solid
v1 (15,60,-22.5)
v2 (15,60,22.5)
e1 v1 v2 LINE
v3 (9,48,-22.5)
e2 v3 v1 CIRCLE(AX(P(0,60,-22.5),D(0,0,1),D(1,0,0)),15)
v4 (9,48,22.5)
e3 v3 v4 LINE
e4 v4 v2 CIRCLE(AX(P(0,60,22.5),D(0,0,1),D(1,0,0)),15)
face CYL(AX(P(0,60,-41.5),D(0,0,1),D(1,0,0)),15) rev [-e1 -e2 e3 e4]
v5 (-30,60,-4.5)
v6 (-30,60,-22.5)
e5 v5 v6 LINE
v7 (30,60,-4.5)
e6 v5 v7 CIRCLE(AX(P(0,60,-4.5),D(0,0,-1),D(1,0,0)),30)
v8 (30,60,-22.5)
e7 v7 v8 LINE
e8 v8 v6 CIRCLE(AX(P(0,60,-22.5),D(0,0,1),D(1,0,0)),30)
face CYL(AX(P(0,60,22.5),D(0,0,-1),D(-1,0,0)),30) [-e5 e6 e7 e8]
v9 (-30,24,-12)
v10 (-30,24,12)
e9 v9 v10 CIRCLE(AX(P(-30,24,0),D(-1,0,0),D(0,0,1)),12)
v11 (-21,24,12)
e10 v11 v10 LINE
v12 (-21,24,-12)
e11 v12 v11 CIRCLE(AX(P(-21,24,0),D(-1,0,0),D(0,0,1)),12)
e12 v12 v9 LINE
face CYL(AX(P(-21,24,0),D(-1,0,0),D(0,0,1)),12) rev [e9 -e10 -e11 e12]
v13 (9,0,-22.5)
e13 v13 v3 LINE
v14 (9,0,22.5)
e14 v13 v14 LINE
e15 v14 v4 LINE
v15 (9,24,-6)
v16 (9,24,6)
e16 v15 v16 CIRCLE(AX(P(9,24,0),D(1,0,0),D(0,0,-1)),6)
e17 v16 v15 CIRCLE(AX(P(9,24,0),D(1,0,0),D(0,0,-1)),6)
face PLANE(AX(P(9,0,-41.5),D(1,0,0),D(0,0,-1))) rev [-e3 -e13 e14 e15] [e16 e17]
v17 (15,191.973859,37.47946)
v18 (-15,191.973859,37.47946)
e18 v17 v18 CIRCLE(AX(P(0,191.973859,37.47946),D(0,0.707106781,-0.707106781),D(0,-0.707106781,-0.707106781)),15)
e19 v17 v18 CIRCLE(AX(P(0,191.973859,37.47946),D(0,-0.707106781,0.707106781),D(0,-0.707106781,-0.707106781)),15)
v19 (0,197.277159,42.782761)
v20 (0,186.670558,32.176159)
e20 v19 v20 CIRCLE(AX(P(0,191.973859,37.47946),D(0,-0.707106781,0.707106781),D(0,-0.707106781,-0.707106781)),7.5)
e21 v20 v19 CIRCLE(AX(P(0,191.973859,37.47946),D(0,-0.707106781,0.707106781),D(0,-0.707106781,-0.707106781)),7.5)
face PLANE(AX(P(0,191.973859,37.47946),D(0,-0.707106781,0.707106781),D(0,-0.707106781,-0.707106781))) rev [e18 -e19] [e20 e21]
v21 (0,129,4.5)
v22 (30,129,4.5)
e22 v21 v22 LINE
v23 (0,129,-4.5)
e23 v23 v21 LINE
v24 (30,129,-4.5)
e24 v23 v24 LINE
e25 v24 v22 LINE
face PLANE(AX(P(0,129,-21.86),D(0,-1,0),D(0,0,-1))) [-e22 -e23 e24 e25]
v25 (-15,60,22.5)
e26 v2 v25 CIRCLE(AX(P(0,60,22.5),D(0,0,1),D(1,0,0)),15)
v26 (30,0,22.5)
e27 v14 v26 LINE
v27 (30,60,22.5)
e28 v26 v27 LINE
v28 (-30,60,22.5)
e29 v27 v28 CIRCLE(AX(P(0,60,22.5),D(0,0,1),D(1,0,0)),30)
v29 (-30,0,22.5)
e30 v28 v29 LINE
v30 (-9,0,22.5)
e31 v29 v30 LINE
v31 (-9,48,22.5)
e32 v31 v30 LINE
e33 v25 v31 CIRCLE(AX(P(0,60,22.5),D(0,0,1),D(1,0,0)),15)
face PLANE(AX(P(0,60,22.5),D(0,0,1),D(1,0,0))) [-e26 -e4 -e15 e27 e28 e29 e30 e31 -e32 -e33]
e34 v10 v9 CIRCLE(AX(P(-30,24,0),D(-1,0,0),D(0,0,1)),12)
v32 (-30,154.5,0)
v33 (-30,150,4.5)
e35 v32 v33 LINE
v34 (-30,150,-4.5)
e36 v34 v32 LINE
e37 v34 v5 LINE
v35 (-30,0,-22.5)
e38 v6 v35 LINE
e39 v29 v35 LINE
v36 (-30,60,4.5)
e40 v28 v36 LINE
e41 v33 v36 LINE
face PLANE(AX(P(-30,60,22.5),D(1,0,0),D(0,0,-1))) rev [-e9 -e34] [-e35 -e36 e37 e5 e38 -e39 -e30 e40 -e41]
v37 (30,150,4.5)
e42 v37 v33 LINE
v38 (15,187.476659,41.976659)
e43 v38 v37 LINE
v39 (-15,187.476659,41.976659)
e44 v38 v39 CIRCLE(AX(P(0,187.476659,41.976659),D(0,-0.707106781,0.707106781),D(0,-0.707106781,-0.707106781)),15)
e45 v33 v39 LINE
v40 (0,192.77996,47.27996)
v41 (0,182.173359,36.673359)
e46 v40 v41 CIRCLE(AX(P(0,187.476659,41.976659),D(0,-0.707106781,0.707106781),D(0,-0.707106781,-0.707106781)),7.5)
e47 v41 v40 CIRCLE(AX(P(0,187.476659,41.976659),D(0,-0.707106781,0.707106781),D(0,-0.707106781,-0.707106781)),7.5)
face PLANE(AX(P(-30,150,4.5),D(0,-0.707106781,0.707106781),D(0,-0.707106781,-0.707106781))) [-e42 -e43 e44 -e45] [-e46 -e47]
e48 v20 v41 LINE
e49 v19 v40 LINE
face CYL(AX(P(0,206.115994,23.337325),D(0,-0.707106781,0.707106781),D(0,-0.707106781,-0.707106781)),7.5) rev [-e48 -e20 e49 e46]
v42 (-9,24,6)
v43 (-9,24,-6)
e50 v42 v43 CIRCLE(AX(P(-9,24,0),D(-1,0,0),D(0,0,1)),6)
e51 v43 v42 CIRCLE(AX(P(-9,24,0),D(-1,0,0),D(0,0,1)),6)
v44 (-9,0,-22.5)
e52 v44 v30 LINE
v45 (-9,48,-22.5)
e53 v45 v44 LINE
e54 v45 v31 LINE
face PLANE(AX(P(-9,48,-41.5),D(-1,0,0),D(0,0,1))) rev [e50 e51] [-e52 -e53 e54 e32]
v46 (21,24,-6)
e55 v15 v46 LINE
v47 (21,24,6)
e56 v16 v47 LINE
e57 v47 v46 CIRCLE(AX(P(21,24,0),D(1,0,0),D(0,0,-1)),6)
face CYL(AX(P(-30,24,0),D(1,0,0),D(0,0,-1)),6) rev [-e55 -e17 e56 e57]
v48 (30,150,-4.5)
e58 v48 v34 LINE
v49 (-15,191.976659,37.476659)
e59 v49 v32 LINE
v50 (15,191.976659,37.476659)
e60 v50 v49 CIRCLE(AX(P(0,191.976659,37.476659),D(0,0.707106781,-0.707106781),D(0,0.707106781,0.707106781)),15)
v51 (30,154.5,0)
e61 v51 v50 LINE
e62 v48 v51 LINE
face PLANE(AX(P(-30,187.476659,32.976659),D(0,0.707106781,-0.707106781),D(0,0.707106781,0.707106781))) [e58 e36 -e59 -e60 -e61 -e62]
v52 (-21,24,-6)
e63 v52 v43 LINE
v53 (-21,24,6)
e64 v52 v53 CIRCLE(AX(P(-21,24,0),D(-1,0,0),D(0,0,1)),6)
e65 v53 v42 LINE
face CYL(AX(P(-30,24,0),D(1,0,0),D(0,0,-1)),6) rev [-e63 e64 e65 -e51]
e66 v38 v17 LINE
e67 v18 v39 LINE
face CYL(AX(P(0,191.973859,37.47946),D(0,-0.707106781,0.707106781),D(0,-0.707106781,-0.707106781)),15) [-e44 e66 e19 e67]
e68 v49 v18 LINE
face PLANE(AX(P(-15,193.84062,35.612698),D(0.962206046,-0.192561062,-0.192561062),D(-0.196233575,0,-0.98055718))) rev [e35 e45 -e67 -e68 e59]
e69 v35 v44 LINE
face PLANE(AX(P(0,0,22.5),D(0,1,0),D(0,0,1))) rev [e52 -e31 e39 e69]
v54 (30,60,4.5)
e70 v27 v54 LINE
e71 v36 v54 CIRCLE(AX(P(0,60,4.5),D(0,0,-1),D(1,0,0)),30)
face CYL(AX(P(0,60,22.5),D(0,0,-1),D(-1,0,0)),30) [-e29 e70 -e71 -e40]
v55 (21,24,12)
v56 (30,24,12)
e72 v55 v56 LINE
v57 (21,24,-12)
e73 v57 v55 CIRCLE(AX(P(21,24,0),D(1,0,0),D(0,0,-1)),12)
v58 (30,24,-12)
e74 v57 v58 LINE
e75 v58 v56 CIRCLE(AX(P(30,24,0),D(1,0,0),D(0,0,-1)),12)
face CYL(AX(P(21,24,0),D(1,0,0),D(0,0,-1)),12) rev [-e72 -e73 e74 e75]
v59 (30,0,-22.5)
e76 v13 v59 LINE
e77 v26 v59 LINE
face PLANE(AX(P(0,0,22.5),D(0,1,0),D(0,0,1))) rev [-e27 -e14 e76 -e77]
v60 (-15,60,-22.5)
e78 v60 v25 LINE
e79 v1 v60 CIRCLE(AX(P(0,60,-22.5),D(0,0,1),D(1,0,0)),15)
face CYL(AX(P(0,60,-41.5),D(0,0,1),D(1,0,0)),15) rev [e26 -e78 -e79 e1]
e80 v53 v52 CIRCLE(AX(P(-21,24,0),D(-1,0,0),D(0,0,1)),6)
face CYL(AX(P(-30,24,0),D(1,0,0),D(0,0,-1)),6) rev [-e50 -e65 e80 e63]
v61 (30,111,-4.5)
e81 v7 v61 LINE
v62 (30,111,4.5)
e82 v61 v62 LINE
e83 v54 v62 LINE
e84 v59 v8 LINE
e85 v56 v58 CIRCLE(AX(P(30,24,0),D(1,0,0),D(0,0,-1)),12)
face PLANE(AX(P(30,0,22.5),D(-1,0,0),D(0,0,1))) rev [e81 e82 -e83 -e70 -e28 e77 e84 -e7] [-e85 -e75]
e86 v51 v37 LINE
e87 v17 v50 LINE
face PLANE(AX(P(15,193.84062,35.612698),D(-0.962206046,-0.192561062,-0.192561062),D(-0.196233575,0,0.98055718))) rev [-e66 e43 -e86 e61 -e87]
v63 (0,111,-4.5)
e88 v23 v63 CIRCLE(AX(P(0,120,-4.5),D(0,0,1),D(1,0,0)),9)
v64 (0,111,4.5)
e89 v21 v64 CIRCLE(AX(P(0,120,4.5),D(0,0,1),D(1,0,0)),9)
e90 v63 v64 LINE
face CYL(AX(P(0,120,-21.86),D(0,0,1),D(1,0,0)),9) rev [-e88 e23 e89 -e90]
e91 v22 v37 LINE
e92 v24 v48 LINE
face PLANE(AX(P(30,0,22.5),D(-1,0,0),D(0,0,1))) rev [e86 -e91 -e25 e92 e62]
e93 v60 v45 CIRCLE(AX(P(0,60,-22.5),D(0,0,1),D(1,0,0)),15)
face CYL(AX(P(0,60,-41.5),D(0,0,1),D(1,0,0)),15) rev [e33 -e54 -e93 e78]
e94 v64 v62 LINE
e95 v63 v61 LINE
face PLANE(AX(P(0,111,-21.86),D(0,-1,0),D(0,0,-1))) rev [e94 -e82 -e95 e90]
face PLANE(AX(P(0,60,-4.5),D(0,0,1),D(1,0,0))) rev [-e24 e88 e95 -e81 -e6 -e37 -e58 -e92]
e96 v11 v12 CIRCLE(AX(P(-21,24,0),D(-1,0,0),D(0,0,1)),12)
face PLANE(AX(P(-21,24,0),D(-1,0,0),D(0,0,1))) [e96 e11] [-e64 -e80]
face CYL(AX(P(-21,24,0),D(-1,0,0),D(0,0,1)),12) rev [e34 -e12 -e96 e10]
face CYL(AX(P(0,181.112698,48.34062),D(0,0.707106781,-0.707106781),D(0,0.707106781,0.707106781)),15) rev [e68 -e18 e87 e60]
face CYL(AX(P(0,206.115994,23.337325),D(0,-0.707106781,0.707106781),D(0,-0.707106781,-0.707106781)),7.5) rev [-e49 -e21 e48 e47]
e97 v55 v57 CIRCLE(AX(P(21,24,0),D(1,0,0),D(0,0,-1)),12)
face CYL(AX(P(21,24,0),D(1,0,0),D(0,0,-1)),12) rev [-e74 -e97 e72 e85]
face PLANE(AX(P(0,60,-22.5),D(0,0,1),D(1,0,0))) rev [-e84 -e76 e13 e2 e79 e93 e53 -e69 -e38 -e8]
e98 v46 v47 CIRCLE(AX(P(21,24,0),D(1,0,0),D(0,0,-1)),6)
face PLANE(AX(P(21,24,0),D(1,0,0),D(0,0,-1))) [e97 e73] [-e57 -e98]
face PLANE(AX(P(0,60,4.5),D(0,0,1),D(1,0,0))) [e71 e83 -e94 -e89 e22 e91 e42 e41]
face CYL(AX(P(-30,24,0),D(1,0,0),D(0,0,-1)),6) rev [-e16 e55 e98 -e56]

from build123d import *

# Parameters (mm, degrees)
CLEVIS_BLOCK_DEPTH         = 22.5
FORK_SLOT_DEPTH            = 64
SIDE_HOLE_A_PROFILE_R      = 12
SIDE_HOLE_A_DEPTH          = 9
SIDE_START                 = -9
SIDE_HOLE_B_PROFILE_R      = 12
SIDE_HOLE_B_DEPTH          = 9
CROSS_HOLE_PROFILE_R       = 6
CROSS_HOLE_DEPTH           = 51
ARM_PLATE_DEPTH            = 4.5
BRACKET_WEB_DEPTH          = 60
PIN_BOSS_PROFILE_R         = 15
PIN_BOSS_DEPTH             = 9
HOOK_SLOT_DEPTH            = 9
BOSS_START                 = -2
BOSS_RECESS_PROFILE_R      = 15
BOSS_RECESS_2MM_DEPTH      = 2
BOSS_START_2               = -16
BOSS_BORE_PROFILE_R        = 15
BOSS_BORE_DEPTH            = 16
BORE_INSERT_BOSS_PROFILE_R = 15
BORE_INSERT_BOSS_DEPTH     = 6.36
INSERT_BORE_PROFILE_R      = 7.5
INSERT_BORE_DEPTH          = 26.36
ARM_TRIM_CUT_DEPTH         = 26.36


with BuildPart() as part:
    # Clevis Block Profile → Clevis Block (new, symmetric)
    with BuildSketch(Plane.XY):
        with BuildLine():
            Line((0, 0), (30, 0))
            Line((30, 0), (30, 60))
            ThreePointArc((30, 60), (0, 90), (-30, 60))
            Line((-30, 60), (-30, 0))
            Line((-30, 0), (0, 0))
        make_face()
    extrude(amount=CLEVIS_BLOCK_DEPTH, both=True)

    # Fork Slot Profile → Fork Slot (cut)
    with BuildSketch(Plane.XY.offset(22.5)):
        with BuildLine():
            Line((0, 0), (9, 0))
            Line((9, 0), (9, 48))
            ThreePointArc((9, 48), (0, 75), (-9, 48))
            Line((-9, 48), (-9, 0))
            Line((-9, 0), (0, 0))
        make_face()
    extrude(amount=-FORK_SLOT_DEPTH, mode=Mode.SUBTRACT)

    # Side Hole A Profile → Side Hole A (cut)
    with BuildSketch(Plane.ZY.offset(30)):
        with Locations((0, 24)):
            Circle(SIDE_HOLE_A_PROFILE_R)
    extrude(amount=-SIDE_HOLE_A_DEPTH, mode=Mode.SUBTRACT)

    # Side Hole B Profile → Side Hole B (cut)
    with BuildSketch(Plane(origin=(30, 0, 0), x_dir=(0, 0, -1), z_dir=(1, 0, 0)).offset(SIDE_START)):
        with Locations(Location((0, 24, 0), (0, 0, 180))):
            Circle(SIDE_HOLE_B_PROFILE_R)
    extrude(amount=SIDE_HOLE_B_DEPTH, mode=Mode.SUBTRACT)

    # Cross Hole Profile → Cross Hole (cut)
    with BuildSketch(Plane(origin=(21, 0, 0), x_dir=(0, 0, -1), z_dir=(1, 0, 0))):
        with Locations(Location((0, 24, 0), (0, 0, 180))):
            Circle(CROSS_HOLE_PROFILE_R)
    extrude(amount=-CROSS_HOLE_DEPTH, mode=Mode.SUBTRACT)

    # Arm Plate Profile → Arm Plate (add, symmetric)
    with BuildSketch(Plane.XY):
        with BuildLine():
            Line((-30, 60), (-30, 150))
            Line((-30, 150), (30, 150))
            Line((30, 150), (30, 60))
            ThreePointArc((30, 60), (0, 90), (-30, 60))
        make_face()
    extrude(amount=ARM_PLATE_DEPTH, both=True)

    # Bracket Web Profile → Bracket Web (add)
    with BuildSketch(Plane(origin=(30, 0, 0), x_dir=(0, 0, -1), z_dir=(1, 0, 0))):
        Polygon((4.5, 150), (-32.976659403, 187.476659403), (-37.476659403, 191.976659403), (-41.976659403, 187.476659403), (-4.5, 150), align=None)
    extrude(amount=-BRACKET_WEB_DEPTH)

    # Pin Boss Profile → Pin Boss (add)
    with BuildSketch(Plane(origin=(0, 72.75, -72.75), x_dir=(1, 0, 0), z_dir=(0, -0.7071067811865479, 0.7071067811865472))):
        with Locations(Location((0, 162.247997693, 0), (0, 0, 270))):
            Circle(PIN_BOSS_PROFILE_R)
    extrude(amount=-PIN_BOSS_DEPTH)

    # Hook Slot Profile → Hook Slot (cut)
    with BuildSketch(Plane(origin=(0, 72.75, -72.75), x_dir=(1, 0, 0), z_dir=(0, -0.7071067811865479, 0.7071067811865472))):
        Polygon((-15, 162.247997693), (-30, 109.247997693), (-30, 162.247997693), align=None)
        Polygon((15, 162.247997693), (30, 109.247997693), (30, 162.247997693), align=None)
    extrude(amount=-HOOK_SLOT_DEPTH, mode=Mode.SUBTRACT)

    # Boss Recess Profile → Boss Recess 2mm (cut)
    with BuildSketch(Plane(origin=(0, 79.113961031, -79.113961031), x_dir=(1, 0, 0), z_dir=(0, 0.7071067811865478, -0.7071067811865472)).offset(BOSS_START)):
        with Locations(Location((0, -162.247997693, 0), (0, 0, 180))):
            Circle(BOSS_RECESS_PROFILE_R)
    extrude(amount=BOSS_RECESS_2MM_DEPTH, mode=Mode.SUBTRACT)

    # Boss Bore Profile → Boss Bore (cut)
    with BuildSketch(Plane(origin=(0, 77.699747468, -77.699747468), x_dir=(1, 0, 0), z_dir=(0, 0.7071067811865479, -0.7071067811865472)).offset(BOSS_START_2)):
        with Locations((0, -162.247997693)):
            Circle(BOSS_BORE_PROFILE_R)
    extrude(amount=BOSS_BORE_DEPTH, mode=Mode.SUBTRACT)

    # Bore Insert Boss Profile → Bore Insert Boss (add)
    with BuildSketch(Plane(origin=(0, 72.75, -72.75), x_dir=(1, 0, 0), z_dir=(0, -0.7071067811865479, 0.7071067811865472))):
        with Locations((0, 162.247997693)):
            Circle(BORE_INSERT_BOSS_PROFILE_R)
    extrude(amount=-BORE_INSERT_BOSS_DEPTH)

    # Insert Bore Profile → Insert Bore (cut)
    with BuildSketch(Plane(origin=(0, 72.75, -72.75), x_dir=(1, 0, 0), z_dir=(0, -0.7071067811865479, 0.7071067811865472))):
        with Locations(Location((0, 162.247997693, 0), (0, 0, 270))):
            Circle(INSERT_BORE_PROFILE_R)
    extrude(amount=-INSERT_BORE_DEPTH, mode=Mode.SUBTRACT)

    # Arm Trim Profile → Arm Trim Cut (cut)
    with BuildSketch(Plane.XY.offset(4.5)):
        with BuildLine():
            Line((0, 111), (30, 111))
            Line((30, 111), (30, 120))
            Line((30, 120), (30, 129))
            Line((30, 129), (0, 129))
            ThreePointArc((0, 129), (-9, 120), (0, 111))
        make_face()
    extrude(amount=-ARM_TRIM_CUT_DEPTH, mode=Mode.SUBTRACT)


solid = part.part
